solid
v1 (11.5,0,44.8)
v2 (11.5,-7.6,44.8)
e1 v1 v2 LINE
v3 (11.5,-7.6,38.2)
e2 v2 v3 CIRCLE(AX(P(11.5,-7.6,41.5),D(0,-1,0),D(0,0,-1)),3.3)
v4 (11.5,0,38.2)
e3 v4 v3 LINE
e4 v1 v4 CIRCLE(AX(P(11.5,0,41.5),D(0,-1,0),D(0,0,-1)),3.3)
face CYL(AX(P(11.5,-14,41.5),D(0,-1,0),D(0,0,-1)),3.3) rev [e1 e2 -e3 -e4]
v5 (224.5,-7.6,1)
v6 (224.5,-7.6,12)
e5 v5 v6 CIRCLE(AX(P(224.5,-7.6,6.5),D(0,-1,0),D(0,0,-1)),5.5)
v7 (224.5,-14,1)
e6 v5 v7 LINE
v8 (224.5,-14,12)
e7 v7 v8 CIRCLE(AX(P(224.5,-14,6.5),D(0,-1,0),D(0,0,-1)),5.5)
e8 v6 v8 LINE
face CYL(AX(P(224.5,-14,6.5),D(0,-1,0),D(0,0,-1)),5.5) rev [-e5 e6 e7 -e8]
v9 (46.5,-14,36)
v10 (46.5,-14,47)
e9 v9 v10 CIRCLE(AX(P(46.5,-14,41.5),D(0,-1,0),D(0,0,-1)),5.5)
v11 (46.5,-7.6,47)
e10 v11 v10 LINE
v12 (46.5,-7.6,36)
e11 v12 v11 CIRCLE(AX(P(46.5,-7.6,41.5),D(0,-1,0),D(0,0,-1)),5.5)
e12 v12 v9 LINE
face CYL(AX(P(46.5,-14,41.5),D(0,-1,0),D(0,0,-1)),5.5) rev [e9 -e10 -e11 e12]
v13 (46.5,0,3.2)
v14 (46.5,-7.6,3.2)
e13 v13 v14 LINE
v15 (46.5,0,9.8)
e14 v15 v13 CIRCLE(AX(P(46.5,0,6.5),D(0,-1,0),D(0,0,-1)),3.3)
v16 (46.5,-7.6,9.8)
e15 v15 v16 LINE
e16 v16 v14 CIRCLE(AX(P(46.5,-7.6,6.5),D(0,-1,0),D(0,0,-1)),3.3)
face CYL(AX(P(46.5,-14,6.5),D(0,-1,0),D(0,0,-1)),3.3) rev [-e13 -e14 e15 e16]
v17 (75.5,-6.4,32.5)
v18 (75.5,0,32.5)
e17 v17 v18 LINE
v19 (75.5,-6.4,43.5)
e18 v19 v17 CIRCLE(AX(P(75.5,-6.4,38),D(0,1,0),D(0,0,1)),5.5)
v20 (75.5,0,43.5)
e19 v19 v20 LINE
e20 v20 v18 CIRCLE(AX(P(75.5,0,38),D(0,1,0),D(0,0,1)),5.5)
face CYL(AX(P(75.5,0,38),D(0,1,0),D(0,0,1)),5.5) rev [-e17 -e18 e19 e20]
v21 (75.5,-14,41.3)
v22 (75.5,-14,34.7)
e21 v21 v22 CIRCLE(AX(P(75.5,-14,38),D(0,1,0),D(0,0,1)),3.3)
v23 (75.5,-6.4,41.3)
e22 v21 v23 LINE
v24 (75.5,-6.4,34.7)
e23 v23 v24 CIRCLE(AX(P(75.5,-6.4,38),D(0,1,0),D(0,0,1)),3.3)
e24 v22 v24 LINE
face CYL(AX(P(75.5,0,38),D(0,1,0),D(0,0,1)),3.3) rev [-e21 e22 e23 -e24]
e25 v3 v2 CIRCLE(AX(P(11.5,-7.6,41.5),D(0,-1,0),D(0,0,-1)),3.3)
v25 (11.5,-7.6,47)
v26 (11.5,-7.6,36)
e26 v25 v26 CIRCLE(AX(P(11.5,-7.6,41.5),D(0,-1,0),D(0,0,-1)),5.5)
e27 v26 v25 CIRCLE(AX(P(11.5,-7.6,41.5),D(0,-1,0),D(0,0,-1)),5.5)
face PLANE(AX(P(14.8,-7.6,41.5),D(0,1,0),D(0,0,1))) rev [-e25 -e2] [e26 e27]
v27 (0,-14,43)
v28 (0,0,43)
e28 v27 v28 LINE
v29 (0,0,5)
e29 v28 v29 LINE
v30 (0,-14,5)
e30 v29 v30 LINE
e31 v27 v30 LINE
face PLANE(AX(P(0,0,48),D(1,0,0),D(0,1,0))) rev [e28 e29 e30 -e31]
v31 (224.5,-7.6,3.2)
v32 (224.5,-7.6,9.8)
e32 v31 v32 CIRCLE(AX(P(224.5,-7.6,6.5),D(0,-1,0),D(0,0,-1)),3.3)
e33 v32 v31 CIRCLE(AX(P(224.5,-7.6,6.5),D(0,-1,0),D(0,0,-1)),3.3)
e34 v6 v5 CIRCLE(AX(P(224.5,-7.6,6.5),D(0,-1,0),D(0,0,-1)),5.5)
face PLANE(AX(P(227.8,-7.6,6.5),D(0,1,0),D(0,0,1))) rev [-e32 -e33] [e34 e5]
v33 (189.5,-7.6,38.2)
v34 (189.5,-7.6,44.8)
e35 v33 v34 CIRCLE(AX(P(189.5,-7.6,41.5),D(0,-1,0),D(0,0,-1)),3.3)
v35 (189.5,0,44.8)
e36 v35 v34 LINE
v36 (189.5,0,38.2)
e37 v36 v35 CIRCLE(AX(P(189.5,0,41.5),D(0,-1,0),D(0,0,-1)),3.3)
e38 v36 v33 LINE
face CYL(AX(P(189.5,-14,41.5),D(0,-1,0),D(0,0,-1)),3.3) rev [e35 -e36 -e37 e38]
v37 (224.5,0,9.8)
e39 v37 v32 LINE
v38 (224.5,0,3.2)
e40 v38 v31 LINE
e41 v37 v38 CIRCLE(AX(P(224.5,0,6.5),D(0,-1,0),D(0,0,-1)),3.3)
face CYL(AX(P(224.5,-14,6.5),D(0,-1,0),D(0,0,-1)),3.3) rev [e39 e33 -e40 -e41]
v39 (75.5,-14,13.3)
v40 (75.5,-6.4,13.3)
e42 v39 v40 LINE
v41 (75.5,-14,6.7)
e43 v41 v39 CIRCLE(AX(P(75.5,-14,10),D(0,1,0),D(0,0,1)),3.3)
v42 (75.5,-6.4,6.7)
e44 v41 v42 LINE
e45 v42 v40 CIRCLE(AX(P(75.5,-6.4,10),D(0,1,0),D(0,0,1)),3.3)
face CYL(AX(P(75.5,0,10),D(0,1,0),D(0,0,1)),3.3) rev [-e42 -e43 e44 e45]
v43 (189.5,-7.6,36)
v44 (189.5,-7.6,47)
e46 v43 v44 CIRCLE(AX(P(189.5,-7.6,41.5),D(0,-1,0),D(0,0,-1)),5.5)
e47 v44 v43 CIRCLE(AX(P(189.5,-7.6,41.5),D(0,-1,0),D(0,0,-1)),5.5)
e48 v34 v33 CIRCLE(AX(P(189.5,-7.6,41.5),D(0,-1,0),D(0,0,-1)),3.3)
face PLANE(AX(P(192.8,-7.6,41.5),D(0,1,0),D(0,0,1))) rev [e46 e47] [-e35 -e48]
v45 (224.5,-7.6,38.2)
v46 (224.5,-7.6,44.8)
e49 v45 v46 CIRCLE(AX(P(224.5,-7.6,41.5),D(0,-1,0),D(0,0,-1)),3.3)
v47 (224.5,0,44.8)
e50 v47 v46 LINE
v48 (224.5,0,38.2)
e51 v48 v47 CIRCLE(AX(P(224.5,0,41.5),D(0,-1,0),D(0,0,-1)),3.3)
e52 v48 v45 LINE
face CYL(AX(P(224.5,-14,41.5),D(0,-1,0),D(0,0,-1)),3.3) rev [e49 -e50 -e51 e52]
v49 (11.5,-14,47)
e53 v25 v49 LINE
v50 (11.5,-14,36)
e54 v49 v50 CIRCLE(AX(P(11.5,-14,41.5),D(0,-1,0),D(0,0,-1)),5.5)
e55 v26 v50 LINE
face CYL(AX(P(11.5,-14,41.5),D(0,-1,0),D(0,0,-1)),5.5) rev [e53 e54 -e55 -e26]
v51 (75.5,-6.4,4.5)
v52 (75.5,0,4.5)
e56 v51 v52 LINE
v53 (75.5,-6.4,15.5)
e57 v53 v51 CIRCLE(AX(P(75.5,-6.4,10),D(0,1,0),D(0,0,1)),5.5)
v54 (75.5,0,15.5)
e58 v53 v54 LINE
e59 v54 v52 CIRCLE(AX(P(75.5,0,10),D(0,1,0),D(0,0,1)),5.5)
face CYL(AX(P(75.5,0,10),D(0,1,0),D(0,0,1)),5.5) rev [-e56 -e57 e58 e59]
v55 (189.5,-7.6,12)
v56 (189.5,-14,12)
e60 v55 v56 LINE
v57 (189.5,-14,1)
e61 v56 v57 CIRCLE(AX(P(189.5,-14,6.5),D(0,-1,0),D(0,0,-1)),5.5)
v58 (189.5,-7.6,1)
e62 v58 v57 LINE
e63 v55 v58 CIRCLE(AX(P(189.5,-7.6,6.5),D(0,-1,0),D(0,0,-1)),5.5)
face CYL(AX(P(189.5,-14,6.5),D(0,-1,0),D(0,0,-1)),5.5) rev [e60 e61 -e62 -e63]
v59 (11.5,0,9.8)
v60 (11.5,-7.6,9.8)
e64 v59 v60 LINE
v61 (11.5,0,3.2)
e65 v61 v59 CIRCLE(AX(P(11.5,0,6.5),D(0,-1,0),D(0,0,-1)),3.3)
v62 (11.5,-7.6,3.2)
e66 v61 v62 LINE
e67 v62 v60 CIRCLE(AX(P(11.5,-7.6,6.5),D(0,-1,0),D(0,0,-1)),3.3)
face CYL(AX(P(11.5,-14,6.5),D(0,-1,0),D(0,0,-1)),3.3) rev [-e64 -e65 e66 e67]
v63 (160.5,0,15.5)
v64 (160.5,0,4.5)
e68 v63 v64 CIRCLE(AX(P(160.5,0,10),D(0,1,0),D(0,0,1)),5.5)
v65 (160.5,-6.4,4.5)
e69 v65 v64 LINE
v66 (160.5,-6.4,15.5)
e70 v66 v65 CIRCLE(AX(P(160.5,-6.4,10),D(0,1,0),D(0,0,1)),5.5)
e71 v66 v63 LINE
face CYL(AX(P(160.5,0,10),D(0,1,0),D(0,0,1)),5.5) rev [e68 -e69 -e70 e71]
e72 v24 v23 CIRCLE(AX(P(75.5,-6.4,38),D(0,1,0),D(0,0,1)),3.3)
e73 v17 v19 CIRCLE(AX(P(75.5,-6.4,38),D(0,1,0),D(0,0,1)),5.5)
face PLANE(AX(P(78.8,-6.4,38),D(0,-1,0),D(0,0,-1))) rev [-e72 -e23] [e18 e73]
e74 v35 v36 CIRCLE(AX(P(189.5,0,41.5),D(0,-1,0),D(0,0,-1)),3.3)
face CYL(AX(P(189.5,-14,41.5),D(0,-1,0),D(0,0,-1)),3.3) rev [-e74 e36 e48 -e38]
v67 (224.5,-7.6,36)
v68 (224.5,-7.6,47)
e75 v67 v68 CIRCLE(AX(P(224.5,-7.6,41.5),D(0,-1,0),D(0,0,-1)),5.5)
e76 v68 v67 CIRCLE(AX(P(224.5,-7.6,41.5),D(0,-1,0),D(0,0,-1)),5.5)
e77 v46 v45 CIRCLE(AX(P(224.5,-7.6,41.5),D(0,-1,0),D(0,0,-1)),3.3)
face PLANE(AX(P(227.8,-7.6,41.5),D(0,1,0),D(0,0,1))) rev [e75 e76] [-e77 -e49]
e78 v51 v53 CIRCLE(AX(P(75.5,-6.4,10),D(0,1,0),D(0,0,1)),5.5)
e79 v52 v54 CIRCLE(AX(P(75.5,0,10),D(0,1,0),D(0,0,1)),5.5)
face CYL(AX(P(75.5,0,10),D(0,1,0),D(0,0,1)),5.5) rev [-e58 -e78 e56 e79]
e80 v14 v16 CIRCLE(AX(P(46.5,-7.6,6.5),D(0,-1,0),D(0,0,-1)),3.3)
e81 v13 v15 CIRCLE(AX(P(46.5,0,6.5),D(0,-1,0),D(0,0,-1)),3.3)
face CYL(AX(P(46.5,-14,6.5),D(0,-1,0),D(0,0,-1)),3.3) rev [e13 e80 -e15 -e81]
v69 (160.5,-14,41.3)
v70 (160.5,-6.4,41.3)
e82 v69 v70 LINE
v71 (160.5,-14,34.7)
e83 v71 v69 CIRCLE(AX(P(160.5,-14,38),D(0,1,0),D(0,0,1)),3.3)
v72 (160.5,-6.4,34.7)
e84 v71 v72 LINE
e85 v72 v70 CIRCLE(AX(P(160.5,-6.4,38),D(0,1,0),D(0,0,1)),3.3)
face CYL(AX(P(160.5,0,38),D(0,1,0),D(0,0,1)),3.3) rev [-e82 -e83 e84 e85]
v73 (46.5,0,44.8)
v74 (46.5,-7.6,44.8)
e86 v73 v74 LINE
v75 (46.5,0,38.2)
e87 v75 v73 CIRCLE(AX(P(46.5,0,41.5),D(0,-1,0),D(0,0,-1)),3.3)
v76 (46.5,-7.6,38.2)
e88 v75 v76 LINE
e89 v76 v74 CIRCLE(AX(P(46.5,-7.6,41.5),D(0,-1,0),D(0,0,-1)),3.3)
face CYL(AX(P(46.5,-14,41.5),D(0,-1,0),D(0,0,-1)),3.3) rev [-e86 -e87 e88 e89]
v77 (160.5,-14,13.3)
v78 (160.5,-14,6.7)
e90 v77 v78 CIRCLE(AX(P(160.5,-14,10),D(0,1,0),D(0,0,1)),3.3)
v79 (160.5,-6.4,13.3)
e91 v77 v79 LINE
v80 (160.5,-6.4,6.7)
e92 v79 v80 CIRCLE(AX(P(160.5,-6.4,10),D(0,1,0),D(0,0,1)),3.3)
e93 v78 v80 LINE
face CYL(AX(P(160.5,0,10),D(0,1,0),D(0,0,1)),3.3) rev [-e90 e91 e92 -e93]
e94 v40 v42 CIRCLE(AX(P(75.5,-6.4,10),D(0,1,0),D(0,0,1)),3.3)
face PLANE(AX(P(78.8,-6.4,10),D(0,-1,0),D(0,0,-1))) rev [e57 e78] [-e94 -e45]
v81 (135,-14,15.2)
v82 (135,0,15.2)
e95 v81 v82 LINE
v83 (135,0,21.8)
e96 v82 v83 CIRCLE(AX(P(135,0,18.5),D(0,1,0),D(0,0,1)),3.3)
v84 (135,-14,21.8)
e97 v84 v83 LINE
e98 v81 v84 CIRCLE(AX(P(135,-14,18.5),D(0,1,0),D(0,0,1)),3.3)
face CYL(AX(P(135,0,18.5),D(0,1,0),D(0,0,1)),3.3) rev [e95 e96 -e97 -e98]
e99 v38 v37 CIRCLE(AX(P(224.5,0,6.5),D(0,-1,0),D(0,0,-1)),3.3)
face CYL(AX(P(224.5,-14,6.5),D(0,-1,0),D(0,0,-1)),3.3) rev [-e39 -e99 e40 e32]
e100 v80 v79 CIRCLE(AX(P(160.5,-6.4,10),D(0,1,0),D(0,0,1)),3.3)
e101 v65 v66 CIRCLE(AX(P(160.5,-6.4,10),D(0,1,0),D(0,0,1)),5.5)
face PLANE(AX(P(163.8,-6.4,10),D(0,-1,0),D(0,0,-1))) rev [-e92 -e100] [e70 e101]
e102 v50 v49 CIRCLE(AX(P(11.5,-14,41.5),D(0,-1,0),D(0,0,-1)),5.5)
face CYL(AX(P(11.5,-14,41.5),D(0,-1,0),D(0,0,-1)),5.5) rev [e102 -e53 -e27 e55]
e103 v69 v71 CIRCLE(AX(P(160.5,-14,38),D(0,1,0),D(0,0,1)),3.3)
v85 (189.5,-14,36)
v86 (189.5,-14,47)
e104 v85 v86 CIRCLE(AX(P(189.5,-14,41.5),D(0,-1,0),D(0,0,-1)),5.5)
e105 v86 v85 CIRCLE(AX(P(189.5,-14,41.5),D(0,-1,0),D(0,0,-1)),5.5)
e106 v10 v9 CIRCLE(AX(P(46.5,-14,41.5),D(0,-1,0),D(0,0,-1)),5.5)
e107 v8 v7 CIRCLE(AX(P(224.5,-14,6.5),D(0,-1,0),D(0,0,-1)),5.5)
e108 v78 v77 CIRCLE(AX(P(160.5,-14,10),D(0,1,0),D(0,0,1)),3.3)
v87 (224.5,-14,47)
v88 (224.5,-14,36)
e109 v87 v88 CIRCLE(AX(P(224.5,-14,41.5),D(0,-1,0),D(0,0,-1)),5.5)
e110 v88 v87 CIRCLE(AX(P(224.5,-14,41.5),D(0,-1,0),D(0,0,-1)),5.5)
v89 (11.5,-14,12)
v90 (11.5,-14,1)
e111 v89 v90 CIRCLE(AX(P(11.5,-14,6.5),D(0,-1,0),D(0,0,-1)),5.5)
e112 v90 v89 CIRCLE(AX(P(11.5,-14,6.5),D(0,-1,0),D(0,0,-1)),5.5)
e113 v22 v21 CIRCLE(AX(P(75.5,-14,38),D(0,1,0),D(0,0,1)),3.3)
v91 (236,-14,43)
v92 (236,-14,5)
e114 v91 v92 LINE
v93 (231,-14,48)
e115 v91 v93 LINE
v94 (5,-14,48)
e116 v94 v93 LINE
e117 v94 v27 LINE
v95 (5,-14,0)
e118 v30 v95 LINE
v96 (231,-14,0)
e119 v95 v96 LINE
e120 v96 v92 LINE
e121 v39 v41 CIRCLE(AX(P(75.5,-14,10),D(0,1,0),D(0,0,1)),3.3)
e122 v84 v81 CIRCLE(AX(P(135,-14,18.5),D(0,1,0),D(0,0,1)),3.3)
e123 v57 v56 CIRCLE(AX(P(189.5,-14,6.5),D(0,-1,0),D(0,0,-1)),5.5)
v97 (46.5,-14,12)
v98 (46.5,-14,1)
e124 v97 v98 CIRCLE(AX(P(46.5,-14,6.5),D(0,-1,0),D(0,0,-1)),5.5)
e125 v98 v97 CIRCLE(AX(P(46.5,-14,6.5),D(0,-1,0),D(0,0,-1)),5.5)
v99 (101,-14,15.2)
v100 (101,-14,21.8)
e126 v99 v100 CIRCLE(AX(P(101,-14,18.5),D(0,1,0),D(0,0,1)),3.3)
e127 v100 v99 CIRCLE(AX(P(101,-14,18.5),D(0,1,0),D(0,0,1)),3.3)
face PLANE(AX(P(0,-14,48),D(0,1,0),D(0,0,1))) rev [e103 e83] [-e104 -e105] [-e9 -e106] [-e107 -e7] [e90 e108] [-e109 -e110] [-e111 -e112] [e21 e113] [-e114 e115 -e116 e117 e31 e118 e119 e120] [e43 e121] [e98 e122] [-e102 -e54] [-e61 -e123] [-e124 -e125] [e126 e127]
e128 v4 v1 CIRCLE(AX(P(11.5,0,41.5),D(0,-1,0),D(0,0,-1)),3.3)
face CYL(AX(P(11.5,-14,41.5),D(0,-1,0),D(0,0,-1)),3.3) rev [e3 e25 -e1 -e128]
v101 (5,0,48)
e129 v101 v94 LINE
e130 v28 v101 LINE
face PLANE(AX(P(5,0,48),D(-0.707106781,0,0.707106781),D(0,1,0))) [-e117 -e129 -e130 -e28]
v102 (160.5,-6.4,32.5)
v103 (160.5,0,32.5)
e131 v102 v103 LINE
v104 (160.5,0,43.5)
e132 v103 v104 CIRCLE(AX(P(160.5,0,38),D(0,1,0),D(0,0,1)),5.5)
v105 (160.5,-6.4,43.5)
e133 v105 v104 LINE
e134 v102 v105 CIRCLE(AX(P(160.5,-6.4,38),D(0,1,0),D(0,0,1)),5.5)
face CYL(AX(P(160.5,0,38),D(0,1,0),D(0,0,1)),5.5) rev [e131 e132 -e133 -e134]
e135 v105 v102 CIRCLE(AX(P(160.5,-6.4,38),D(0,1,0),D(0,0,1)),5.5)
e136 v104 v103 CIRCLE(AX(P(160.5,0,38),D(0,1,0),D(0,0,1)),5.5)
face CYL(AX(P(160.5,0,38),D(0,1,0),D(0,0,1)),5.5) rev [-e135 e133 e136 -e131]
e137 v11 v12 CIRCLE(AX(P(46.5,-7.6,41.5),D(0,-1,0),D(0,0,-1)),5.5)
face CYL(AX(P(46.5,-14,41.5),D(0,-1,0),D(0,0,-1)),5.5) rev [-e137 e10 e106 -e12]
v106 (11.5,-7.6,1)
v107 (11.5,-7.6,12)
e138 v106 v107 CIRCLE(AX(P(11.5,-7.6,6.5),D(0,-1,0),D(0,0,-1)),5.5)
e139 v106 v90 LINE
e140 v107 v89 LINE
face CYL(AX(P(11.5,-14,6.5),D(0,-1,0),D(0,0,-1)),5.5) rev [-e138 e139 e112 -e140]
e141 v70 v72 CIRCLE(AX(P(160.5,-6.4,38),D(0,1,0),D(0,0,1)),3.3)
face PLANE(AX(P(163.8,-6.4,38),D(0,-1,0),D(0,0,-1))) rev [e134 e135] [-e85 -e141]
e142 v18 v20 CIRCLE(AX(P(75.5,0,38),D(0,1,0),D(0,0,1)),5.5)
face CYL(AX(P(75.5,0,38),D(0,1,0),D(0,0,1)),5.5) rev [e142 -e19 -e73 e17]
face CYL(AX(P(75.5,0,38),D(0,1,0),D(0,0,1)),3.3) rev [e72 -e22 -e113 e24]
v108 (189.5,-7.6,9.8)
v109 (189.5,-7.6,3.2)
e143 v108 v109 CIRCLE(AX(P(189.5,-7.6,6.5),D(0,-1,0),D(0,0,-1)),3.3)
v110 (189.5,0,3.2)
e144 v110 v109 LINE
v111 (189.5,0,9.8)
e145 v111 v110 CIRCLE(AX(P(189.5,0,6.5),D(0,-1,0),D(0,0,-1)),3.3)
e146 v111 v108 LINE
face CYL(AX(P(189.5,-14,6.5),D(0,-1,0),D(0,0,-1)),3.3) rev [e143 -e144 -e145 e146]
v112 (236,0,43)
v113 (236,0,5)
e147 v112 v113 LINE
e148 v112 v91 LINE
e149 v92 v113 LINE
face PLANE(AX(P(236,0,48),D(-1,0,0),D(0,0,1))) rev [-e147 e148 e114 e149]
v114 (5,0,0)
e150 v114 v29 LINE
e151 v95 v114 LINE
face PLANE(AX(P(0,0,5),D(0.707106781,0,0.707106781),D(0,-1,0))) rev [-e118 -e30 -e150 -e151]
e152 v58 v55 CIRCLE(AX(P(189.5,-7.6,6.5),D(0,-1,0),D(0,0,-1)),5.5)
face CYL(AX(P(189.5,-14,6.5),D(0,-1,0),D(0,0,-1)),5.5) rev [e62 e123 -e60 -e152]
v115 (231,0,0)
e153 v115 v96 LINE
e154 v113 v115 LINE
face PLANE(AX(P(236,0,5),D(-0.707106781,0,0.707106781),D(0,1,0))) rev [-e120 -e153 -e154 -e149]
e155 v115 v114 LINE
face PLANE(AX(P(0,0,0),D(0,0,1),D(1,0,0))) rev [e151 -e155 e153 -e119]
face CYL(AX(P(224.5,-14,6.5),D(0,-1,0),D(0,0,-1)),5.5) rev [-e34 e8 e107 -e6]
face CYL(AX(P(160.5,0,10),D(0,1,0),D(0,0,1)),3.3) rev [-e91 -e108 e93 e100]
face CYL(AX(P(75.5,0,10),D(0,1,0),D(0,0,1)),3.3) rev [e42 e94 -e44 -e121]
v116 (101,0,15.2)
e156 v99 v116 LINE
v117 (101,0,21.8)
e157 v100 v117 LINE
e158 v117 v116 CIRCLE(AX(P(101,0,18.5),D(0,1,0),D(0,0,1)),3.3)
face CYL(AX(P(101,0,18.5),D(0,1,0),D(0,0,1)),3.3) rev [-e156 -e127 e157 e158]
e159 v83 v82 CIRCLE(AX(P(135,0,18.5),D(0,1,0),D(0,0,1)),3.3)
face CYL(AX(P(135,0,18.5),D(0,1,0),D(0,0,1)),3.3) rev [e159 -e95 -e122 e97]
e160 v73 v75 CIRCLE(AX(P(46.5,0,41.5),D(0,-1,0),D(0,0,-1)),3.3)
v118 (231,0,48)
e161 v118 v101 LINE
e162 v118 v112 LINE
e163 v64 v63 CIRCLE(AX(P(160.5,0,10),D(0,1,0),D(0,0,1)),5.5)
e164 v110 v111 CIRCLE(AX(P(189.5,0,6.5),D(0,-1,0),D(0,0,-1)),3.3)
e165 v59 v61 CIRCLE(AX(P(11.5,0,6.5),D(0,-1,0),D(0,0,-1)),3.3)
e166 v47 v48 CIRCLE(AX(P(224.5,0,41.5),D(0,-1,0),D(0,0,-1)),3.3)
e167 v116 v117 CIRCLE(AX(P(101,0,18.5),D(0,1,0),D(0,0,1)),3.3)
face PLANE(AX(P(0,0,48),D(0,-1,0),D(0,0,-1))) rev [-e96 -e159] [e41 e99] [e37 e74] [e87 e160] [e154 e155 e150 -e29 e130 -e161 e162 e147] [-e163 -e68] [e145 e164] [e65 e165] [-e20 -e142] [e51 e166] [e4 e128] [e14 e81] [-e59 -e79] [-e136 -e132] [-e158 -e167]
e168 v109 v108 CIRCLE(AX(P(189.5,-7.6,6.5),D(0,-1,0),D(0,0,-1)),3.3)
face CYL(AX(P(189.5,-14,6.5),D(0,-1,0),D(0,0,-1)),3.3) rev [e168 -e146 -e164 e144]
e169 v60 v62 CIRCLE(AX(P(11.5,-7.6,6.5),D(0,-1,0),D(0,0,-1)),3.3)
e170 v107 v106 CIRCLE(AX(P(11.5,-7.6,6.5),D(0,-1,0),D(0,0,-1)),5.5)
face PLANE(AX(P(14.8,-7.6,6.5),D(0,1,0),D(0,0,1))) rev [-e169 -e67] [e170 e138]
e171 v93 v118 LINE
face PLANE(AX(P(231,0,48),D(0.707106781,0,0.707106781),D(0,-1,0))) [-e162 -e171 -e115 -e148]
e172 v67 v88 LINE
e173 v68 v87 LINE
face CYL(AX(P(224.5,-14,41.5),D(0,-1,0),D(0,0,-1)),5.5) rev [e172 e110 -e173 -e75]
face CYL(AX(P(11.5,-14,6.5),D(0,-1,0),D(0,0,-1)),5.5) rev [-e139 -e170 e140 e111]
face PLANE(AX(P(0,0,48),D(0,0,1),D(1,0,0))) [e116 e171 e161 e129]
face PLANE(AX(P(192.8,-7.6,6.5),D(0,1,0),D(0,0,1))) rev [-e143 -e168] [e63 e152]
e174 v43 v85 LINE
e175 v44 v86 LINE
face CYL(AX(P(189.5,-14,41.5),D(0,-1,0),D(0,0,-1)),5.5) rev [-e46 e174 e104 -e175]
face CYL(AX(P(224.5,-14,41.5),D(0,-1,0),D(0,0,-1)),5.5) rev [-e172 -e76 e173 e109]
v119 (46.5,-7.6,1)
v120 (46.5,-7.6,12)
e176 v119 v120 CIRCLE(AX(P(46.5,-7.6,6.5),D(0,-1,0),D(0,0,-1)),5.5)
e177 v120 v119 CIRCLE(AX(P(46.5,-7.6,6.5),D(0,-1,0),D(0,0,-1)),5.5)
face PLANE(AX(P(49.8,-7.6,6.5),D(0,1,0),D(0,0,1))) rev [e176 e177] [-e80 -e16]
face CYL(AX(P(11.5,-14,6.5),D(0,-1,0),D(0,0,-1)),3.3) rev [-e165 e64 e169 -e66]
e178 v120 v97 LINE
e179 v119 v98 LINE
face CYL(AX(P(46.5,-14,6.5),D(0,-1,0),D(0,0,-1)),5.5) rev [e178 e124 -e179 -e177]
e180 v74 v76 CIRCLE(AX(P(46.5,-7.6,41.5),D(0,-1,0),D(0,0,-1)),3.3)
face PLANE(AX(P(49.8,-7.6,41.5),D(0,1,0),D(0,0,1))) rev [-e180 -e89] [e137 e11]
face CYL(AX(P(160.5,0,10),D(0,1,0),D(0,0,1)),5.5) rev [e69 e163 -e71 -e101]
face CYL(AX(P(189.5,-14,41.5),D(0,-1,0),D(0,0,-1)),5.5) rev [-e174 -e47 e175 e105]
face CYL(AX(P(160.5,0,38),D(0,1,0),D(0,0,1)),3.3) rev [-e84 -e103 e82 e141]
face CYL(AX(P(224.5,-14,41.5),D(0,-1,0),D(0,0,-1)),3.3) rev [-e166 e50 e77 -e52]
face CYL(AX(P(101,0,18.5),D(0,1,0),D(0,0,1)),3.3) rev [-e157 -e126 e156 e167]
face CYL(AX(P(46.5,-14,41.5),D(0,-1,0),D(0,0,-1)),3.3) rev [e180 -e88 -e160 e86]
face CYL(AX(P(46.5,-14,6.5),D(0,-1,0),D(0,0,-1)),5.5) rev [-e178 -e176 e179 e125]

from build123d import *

# Parameters (mm, degrees)
SKETCH_2_W                   = 236
SKETCH_2_H                   = 14
EXTRUDE_1_DEPTH              = 48
HOLE_WIZARD_M6_1_D           = 6.6
HOLE_WIZARD_M6_1_DEPTH       = 14
HOLE_WIZARD_M6_1_CBORE_D     = 11
HOLE_WIZARD_M6_1_CBORE_DEPTH = 6.4
HOLE_WIZARD_M6_1_TIP         = 1.982840043
CHAMFER_1_SIZE               = 5
HOLE_WIZARD_M6_2_D           = 6.6
HOLE_WIZARD_M6_2_DEPTH       = 14
HOLE_WIZARD_M6_2_CBORE_D     = 11
HOLE_WIZARD_M6_2_CBORE_DEPTH = 6.4
HOLE_WIZARD_M6_2_TIP         = 1.982840043
HOLE_WIZARD_M6_1_2_D         = 6.6


with BuildPart() as part:
    # 草图2 → 凸台-拉伸1 (new body)
    with BuildSketch(Plane.XY):
        with Locations((118, -7)):
            Rectangle(SKETCH_2_W, SKETCH_2_H)
    extrude(amount=EXTRUDE_1_DEPTH)

    # Hole Wizard M6 _1
    with Locations(Plane(origin=(0, -14, 0), x_dir=(-1, 0, 0), z_dir=(0, -1, 0))):
        with Locations((-224.5, -6.5), (-189.5, -6.5), (-189.5, -41.5), (-224.5, -41.5), (-11.5, -41.5), (-46.5, -41.5), (-46.5, -6.5), (-11.5, -6.5)):
            CounterBoreHole(HOLE_WIZARD_M6_1_D / 2, HOLE_WIZARD_M6_1_CBORE_D / 2, HOLE_WIZARD_M6_1_CBORE_DEPTH, depth=HOLE_WIZARD_M6_1_DEPTH)
            with Locations((0, 0, -(HOLE_WIZARD_M6_1_DEPTH + HOLE_WIZARD_M6_1_TIP / 2))):  # 118° drill point
                Cone(0, HOLE_WIZARD_M6_1_D / 2, HOLE_WIZARD_M6_1_TIP, mode=Mode.SUBTRACT)

    # 倒角1
    chamfer_1_edges = [part.edges().sort_by_distance(p)[0] for p in [
        (236, -7, 48),
        (0, -7, 48),
        (236, -7, 0),
        (0, -7, 0),
    ]]
    chamfer(chamfer_1_edges, length=CHAMFER_1_SIZE)

    # M6 六角凹头螺钉的柱形沉头孔2
    with Locations(Plane(origin=(0, 0, 0), x_dir=(1, 0, 0), z_dir=(0, 1, 0))):
        with Locations((75.5, -10), (160.5, -10), (75.5, -38), (160.5, -38)):
            CounterBoreHole(HOLE_WIZARD_M6_2_D / 2, HOLE_WIZARD_M6_2_CBORE_D / 2, HOLE_WIZARD_M6_2_CBORE_DEPTH, depth=HOLE_WIZARD_M6_2_DEPTH)
            with Locations((0, 0, -(HOLE_WIZARD_M6_2_DEPTH + HOLE_WIZARD_M6_2_TIP / 2))):  # 118° drill point
                Cone(0, HOLE_WIZARD_M6_2_D / 2, HOLE_WIZARD_M6_2_TIP, mode=Mode.SUBTRACT)

    # Hole Wizard M6 _1 2 (through all)
    with Locations(Plane(origin=(0, 0, 0), x_dir=(1, 0, 0), z_dir=(0, 1, 0))):
        with Locations((101, -18.5), (135, -18.5)):
            Hole(HOLE_WIZARD_M6_1_2_D / 2)


solid = part.part
